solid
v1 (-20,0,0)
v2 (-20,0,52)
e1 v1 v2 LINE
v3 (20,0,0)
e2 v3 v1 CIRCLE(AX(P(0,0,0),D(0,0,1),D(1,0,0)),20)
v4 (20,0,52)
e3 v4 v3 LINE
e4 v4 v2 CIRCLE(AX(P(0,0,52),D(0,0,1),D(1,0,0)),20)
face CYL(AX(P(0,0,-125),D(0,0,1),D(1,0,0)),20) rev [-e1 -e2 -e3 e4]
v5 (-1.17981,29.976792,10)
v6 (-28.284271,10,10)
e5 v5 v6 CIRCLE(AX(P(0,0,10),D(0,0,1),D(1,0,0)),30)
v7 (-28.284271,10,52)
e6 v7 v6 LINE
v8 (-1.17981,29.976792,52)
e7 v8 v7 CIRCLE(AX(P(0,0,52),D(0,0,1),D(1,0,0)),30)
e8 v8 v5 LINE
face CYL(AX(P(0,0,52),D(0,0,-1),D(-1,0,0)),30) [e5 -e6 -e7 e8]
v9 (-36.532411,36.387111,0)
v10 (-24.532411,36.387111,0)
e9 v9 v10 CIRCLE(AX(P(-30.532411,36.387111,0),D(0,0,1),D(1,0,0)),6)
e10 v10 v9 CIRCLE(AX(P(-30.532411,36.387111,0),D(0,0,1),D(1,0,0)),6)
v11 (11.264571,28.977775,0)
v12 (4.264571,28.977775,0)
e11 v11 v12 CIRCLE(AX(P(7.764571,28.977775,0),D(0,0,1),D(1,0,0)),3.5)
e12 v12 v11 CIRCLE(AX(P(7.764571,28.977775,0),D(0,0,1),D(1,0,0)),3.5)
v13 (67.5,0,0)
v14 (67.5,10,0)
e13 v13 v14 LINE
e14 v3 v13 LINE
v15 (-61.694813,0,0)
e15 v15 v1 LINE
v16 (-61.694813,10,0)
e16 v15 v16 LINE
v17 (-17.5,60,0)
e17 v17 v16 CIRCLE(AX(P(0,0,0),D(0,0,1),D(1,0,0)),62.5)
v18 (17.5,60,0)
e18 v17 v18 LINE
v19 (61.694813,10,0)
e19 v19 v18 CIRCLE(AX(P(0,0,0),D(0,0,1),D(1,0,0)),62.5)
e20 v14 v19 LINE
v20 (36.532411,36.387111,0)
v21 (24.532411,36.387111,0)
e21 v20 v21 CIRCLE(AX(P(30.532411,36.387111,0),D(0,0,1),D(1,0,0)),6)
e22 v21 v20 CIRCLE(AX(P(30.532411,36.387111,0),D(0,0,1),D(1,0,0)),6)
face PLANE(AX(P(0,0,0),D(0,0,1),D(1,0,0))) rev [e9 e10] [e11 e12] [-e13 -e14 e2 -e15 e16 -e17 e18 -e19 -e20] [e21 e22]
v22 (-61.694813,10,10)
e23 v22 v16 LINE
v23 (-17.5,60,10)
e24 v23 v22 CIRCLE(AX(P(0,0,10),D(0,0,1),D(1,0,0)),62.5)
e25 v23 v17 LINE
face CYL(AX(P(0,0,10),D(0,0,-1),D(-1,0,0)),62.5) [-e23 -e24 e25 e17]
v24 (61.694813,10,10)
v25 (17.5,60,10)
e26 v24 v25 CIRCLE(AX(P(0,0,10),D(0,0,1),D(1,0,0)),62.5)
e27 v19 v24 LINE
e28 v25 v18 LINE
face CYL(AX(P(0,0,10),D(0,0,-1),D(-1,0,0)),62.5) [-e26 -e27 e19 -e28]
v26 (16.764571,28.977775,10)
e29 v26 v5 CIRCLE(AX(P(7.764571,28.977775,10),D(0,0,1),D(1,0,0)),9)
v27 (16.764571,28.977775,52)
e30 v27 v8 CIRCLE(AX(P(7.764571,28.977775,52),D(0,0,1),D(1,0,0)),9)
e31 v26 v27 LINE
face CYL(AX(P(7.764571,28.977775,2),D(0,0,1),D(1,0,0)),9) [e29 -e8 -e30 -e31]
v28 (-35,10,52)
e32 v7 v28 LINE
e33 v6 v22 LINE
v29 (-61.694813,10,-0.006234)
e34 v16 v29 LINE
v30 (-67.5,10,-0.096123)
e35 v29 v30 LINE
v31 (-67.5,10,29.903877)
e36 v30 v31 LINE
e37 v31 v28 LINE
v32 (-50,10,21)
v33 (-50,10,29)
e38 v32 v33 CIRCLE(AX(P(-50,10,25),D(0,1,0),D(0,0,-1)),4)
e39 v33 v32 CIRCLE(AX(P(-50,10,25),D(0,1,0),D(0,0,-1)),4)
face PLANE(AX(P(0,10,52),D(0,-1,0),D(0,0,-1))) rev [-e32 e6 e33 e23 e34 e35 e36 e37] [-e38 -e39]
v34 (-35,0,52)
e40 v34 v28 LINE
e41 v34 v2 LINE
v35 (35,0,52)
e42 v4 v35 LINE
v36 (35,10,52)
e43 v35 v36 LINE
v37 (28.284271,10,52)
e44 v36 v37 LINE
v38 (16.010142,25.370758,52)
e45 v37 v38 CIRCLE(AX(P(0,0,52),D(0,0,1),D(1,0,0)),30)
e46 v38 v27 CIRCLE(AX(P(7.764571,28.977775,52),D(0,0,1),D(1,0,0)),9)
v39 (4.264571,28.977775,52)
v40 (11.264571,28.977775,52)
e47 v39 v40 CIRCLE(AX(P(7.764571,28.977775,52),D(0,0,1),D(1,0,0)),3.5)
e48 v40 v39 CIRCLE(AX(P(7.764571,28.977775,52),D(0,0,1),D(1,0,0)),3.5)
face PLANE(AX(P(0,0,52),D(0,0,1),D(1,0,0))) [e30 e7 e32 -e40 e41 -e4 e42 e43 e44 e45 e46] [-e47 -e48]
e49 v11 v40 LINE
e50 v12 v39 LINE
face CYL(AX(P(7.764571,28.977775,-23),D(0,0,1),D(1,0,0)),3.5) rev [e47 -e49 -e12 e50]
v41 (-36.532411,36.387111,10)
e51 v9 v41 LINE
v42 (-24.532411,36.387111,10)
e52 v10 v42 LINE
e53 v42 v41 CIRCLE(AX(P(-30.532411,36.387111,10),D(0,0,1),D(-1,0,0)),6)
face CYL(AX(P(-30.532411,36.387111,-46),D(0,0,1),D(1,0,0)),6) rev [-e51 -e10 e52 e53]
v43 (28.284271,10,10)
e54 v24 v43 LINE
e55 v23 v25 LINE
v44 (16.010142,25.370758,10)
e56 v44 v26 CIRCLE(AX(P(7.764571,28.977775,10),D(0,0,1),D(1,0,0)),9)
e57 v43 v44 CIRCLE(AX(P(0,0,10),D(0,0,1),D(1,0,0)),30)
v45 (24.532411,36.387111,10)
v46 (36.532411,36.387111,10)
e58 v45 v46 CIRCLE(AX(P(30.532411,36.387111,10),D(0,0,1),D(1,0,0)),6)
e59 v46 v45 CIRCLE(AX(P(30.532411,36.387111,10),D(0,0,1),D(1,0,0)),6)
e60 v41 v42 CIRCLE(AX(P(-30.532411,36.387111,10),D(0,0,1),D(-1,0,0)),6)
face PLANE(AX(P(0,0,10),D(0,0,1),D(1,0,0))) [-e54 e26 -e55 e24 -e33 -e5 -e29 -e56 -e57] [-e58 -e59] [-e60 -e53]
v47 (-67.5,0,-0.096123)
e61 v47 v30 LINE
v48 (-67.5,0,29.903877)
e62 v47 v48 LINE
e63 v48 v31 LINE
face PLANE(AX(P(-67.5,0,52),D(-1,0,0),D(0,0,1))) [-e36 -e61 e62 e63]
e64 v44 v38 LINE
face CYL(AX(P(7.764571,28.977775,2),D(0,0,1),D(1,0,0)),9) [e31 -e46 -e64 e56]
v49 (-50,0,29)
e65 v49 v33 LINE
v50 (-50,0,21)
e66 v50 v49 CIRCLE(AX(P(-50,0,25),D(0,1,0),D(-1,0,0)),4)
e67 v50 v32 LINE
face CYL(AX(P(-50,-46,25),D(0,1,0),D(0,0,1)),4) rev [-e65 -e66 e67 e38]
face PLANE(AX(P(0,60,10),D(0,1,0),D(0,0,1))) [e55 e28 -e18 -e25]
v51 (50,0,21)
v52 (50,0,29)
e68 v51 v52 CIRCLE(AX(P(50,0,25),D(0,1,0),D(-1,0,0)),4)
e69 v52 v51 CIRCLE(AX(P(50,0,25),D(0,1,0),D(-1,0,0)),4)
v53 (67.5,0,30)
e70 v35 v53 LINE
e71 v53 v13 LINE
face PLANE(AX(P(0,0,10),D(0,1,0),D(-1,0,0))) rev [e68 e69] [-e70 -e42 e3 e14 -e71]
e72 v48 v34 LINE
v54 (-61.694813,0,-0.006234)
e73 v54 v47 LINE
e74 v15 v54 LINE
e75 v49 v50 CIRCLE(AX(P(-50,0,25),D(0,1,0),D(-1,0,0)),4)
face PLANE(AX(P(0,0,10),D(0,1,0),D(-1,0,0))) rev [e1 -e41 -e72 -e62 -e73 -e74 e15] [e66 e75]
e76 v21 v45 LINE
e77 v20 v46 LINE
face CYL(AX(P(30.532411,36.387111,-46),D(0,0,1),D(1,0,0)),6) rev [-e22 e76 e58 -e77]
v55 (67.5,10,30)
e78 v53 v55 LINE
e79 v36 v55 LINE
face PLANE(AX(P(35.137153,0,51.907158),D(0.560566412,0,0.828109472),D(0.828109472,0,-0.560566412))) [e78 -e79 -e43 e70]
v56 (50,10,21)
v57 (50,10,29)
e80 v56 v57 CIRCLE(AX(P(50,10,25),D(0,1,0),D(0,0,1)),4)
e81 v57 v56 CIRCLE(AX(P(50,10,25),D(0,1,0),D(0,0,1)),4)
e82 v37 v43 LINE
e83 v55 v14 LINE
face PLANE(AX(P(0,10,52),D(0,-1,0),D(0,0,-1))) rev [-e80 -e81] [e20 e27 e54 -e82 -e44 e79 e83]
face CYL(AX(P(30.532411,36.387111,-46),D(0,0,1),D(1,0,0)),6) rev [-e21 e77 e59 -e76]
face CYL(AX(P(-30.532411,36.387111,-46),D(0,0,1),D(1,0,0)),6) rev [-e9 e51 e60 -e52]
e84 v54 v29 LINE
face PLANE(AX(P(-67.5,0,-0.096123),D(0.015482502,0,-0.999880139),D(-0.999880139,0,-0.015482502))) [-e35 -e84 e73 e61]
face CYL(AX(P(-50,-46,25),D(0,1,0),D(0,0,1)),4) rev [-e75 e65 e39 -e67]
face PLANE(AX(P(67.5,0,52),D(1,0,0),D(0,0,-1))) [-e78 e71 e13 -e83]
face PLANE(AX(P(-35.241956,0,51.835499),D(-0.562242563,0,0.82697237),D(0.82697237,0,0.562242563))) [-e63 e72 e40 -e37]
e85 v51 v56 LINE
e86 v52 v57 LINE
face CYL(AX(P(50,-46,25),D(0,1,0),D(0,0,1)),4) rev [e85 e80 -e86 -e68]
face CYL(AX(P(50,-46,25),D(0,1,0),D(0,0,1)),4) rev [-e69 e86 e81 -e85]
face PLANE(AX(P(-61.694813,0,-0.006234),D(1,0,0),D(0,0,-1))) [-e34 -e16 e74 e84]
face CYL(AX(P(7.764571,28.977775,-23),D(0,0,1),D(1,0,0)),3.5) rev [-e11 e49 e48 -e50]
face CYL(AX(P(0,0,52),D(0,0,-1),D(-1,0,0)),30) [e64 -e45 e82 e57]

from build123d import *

# Parameters (mm, degrees)
BASE_FLANGE_DEPTH      = 10
BEARING_HOUSING_DEPTH  = 42
BORE_40_SKETCH_R       = 20
BORE_40_DEPTH          = 177
BACK_PLATE_DEPTH       = 10
BACK_PLATE_TRIM_DEPTH  = 10
HOLES_2X_8_SKETCH_R    = 4
HOLES_2X_8_DEPTH       = 56
HOLES_2X_12_SKETCH_R   = 6
HOLES_2X_12_DEPTH      = 56
HINGE_BOSS_18_SKETCH_R = 9
HINGE_BOSS_18_DEPTH    = 50
PIN_HOLE_7_SKETCH_R    = 3.5
PIN_HOLE_7_DEPTH       = 75


with BuildPart() as part:
    # Base Flange Sketch → Base Flange (new body)
    with BuildSketch(Plane.XY):
        with BuildLine():
            Line((-62.5, 0), (0, 0))
            Line((0, 0), (38.178366278, 0))
            Line((38.178366278, 0), (62.5, 0))
            ThreePointArc((62.5, 0), (50, 37.5), (17.5, 60))
            Line((17.5, 60), (0, 60))
            Line((0, 60), (-17.5, 60))
            ThreePointArc((-17.5, 60), (-50, 37.5), (-62.5, 0))
        make_face()
    extrude(amount=BASE_FLANGE_DEPTH)

    # Bearing Housing Sketch → Bearing Housing (add)
    with BuildSketch(Plane.XY.offset(10)):
        with BuildLine():
            Line((30, 0), (62.5, 0))
            ThreePointArc((62.5, 0), (62.298378138, 5.016181951), (61.694813396, 10))
            Line((61.694813396, 10), (28.284271247, 10))
            ThreePointArc((28.284271247, 10), (29.56795679, 5.073059362), (30, 0))
        make_face()
        with BuildLine():
            Line((-30, 0), (30, 0))
            ThreePointArc((30, 0), (29.56795679, 5.073059362), (28.284271247, 10))
            ThreePointArc((28.284271247, 10), (0, 30), (-28.284271247, 10))
            ThreePointArc((-28.284271247, 10), (-29.56795679, 5.073059362), (-30, 0))
        make_face()
        with BuildLine():
            Line((-62.5, 0), (-30, 0))
            ThreePointArc((-30, 0), (-29.56795679, 5.073059362), (-28.284271247, 10))
            Line((-28.284271247, 10), (-61.694813396, 10))
            ThreePointArc((-61.694813396, 10), (-62.298378138, 5.016181951), (-62.5, 0))
        make_face()
    extrude(amount=BEARING_HOUSING_DEPTH)

    # Bore Ø40 Sketch → Bore Ø40 (cut)
    with BuildSketch(Plane.XY.offset(52)):
        Circle(BORE_40_SKETCH_R)
    extrude(amount=-BORE_40_DEPTH, mode=Mode.SUBTRACT)

    # Back Plate Sketch → Back Plate (add)
    with BuildSketch(Plane(origin=(0, 10, 0), x_dir=(1, 0, 0), z_dir=(0, 1, 0))):
        Polygon((61.694813396, -52), (67.5, -52), (67.5, 0), (62.5, 0), (61.694813396, 0), align=None)
        Polygon((-67.5, -52), (-61.694813396, -52), (-61.694813396, 0.006233525), (-67.5, 0.096123111), align=None)
    extrude(amount=-BACK_PLATE_DEPTH)

    # Back Plate Trim Sketch → Back Plate Trim (cut)
    with BuildSketch(Plane(origin=(0, 10, 0), x_dir=(1, 0, 0), z_dir=(0, 1, 0))):
        Polygon((67.5, -30), (35, -52), (67.5, -52), align=None)
        Polygon((-67.5, -52), (-67.5, -29.903876889), (-35, -52), align=None)
    extrude(amount=-BACK_PLATE_TRIM_DEPTH, mode=Mode.SUBTRACT)

    # Holes 2xØ8 Sketch → Holes 2xØ8 (cut)
    with BuildSketch(Plane(origin=(0, 10, 0), x_dir=(1, 0, 0), z_dir=(0, 1, 0))):
        with Locations(Location((50, -25, 0), (0, 0, 270))):
            Circle(HOLES_2X_8_SKETCH_R)
        with Locations(Location((-50, -25, 0), (0, 0, 180))):
            Circle(HOLES_2X_8_SKETCH_R)
    extrude(amount=-HOLES_2X_8_DEPTH, mode=Mode.SUBTRACT)

    # Holes 2xØ12 Sketch → Holes 2xØ12 (cut)
    with BuildSketch(Plane.XY.offset(10)):
        with Locations((30.53241146, 36.387111048)):
            Circle(HOLES_2X_12_SKETCH_R)
        with Locations((-30.53241146, 36.387111048)):
            Circle(HOLES_2X_12_SKETCH_R)
    extrude(amount=-HOLES_2X_12_DEPTH, mode=Mode.SUBTRACT)

    # Hinge Boss Ø18 Sketch → Hinge Boss Ø18 (add)
    with BuildSketch(Plane.XY.offset(52)):
        with Locations((7.764571353, 28.977774789)):
            Circle(HINGE_BOSS_18_SKETCH_R)
    extrude(amount=-HINGE_BOSS_18_DEPTH)

    # Pin Hole Ø7 Sketch → Pin Hole Ø7 (cut)
    with BuildSketch(Plane.XY.offset(52)):
        with Locations((7.764571353, 28.977774789)):
            Circle(PIN_HOLE_7_SKETCH_R)
    extrude(amount=-PIN_HOLE_7_DEPTH, mode=Mode.SUBTRACT)


solid = part.part
